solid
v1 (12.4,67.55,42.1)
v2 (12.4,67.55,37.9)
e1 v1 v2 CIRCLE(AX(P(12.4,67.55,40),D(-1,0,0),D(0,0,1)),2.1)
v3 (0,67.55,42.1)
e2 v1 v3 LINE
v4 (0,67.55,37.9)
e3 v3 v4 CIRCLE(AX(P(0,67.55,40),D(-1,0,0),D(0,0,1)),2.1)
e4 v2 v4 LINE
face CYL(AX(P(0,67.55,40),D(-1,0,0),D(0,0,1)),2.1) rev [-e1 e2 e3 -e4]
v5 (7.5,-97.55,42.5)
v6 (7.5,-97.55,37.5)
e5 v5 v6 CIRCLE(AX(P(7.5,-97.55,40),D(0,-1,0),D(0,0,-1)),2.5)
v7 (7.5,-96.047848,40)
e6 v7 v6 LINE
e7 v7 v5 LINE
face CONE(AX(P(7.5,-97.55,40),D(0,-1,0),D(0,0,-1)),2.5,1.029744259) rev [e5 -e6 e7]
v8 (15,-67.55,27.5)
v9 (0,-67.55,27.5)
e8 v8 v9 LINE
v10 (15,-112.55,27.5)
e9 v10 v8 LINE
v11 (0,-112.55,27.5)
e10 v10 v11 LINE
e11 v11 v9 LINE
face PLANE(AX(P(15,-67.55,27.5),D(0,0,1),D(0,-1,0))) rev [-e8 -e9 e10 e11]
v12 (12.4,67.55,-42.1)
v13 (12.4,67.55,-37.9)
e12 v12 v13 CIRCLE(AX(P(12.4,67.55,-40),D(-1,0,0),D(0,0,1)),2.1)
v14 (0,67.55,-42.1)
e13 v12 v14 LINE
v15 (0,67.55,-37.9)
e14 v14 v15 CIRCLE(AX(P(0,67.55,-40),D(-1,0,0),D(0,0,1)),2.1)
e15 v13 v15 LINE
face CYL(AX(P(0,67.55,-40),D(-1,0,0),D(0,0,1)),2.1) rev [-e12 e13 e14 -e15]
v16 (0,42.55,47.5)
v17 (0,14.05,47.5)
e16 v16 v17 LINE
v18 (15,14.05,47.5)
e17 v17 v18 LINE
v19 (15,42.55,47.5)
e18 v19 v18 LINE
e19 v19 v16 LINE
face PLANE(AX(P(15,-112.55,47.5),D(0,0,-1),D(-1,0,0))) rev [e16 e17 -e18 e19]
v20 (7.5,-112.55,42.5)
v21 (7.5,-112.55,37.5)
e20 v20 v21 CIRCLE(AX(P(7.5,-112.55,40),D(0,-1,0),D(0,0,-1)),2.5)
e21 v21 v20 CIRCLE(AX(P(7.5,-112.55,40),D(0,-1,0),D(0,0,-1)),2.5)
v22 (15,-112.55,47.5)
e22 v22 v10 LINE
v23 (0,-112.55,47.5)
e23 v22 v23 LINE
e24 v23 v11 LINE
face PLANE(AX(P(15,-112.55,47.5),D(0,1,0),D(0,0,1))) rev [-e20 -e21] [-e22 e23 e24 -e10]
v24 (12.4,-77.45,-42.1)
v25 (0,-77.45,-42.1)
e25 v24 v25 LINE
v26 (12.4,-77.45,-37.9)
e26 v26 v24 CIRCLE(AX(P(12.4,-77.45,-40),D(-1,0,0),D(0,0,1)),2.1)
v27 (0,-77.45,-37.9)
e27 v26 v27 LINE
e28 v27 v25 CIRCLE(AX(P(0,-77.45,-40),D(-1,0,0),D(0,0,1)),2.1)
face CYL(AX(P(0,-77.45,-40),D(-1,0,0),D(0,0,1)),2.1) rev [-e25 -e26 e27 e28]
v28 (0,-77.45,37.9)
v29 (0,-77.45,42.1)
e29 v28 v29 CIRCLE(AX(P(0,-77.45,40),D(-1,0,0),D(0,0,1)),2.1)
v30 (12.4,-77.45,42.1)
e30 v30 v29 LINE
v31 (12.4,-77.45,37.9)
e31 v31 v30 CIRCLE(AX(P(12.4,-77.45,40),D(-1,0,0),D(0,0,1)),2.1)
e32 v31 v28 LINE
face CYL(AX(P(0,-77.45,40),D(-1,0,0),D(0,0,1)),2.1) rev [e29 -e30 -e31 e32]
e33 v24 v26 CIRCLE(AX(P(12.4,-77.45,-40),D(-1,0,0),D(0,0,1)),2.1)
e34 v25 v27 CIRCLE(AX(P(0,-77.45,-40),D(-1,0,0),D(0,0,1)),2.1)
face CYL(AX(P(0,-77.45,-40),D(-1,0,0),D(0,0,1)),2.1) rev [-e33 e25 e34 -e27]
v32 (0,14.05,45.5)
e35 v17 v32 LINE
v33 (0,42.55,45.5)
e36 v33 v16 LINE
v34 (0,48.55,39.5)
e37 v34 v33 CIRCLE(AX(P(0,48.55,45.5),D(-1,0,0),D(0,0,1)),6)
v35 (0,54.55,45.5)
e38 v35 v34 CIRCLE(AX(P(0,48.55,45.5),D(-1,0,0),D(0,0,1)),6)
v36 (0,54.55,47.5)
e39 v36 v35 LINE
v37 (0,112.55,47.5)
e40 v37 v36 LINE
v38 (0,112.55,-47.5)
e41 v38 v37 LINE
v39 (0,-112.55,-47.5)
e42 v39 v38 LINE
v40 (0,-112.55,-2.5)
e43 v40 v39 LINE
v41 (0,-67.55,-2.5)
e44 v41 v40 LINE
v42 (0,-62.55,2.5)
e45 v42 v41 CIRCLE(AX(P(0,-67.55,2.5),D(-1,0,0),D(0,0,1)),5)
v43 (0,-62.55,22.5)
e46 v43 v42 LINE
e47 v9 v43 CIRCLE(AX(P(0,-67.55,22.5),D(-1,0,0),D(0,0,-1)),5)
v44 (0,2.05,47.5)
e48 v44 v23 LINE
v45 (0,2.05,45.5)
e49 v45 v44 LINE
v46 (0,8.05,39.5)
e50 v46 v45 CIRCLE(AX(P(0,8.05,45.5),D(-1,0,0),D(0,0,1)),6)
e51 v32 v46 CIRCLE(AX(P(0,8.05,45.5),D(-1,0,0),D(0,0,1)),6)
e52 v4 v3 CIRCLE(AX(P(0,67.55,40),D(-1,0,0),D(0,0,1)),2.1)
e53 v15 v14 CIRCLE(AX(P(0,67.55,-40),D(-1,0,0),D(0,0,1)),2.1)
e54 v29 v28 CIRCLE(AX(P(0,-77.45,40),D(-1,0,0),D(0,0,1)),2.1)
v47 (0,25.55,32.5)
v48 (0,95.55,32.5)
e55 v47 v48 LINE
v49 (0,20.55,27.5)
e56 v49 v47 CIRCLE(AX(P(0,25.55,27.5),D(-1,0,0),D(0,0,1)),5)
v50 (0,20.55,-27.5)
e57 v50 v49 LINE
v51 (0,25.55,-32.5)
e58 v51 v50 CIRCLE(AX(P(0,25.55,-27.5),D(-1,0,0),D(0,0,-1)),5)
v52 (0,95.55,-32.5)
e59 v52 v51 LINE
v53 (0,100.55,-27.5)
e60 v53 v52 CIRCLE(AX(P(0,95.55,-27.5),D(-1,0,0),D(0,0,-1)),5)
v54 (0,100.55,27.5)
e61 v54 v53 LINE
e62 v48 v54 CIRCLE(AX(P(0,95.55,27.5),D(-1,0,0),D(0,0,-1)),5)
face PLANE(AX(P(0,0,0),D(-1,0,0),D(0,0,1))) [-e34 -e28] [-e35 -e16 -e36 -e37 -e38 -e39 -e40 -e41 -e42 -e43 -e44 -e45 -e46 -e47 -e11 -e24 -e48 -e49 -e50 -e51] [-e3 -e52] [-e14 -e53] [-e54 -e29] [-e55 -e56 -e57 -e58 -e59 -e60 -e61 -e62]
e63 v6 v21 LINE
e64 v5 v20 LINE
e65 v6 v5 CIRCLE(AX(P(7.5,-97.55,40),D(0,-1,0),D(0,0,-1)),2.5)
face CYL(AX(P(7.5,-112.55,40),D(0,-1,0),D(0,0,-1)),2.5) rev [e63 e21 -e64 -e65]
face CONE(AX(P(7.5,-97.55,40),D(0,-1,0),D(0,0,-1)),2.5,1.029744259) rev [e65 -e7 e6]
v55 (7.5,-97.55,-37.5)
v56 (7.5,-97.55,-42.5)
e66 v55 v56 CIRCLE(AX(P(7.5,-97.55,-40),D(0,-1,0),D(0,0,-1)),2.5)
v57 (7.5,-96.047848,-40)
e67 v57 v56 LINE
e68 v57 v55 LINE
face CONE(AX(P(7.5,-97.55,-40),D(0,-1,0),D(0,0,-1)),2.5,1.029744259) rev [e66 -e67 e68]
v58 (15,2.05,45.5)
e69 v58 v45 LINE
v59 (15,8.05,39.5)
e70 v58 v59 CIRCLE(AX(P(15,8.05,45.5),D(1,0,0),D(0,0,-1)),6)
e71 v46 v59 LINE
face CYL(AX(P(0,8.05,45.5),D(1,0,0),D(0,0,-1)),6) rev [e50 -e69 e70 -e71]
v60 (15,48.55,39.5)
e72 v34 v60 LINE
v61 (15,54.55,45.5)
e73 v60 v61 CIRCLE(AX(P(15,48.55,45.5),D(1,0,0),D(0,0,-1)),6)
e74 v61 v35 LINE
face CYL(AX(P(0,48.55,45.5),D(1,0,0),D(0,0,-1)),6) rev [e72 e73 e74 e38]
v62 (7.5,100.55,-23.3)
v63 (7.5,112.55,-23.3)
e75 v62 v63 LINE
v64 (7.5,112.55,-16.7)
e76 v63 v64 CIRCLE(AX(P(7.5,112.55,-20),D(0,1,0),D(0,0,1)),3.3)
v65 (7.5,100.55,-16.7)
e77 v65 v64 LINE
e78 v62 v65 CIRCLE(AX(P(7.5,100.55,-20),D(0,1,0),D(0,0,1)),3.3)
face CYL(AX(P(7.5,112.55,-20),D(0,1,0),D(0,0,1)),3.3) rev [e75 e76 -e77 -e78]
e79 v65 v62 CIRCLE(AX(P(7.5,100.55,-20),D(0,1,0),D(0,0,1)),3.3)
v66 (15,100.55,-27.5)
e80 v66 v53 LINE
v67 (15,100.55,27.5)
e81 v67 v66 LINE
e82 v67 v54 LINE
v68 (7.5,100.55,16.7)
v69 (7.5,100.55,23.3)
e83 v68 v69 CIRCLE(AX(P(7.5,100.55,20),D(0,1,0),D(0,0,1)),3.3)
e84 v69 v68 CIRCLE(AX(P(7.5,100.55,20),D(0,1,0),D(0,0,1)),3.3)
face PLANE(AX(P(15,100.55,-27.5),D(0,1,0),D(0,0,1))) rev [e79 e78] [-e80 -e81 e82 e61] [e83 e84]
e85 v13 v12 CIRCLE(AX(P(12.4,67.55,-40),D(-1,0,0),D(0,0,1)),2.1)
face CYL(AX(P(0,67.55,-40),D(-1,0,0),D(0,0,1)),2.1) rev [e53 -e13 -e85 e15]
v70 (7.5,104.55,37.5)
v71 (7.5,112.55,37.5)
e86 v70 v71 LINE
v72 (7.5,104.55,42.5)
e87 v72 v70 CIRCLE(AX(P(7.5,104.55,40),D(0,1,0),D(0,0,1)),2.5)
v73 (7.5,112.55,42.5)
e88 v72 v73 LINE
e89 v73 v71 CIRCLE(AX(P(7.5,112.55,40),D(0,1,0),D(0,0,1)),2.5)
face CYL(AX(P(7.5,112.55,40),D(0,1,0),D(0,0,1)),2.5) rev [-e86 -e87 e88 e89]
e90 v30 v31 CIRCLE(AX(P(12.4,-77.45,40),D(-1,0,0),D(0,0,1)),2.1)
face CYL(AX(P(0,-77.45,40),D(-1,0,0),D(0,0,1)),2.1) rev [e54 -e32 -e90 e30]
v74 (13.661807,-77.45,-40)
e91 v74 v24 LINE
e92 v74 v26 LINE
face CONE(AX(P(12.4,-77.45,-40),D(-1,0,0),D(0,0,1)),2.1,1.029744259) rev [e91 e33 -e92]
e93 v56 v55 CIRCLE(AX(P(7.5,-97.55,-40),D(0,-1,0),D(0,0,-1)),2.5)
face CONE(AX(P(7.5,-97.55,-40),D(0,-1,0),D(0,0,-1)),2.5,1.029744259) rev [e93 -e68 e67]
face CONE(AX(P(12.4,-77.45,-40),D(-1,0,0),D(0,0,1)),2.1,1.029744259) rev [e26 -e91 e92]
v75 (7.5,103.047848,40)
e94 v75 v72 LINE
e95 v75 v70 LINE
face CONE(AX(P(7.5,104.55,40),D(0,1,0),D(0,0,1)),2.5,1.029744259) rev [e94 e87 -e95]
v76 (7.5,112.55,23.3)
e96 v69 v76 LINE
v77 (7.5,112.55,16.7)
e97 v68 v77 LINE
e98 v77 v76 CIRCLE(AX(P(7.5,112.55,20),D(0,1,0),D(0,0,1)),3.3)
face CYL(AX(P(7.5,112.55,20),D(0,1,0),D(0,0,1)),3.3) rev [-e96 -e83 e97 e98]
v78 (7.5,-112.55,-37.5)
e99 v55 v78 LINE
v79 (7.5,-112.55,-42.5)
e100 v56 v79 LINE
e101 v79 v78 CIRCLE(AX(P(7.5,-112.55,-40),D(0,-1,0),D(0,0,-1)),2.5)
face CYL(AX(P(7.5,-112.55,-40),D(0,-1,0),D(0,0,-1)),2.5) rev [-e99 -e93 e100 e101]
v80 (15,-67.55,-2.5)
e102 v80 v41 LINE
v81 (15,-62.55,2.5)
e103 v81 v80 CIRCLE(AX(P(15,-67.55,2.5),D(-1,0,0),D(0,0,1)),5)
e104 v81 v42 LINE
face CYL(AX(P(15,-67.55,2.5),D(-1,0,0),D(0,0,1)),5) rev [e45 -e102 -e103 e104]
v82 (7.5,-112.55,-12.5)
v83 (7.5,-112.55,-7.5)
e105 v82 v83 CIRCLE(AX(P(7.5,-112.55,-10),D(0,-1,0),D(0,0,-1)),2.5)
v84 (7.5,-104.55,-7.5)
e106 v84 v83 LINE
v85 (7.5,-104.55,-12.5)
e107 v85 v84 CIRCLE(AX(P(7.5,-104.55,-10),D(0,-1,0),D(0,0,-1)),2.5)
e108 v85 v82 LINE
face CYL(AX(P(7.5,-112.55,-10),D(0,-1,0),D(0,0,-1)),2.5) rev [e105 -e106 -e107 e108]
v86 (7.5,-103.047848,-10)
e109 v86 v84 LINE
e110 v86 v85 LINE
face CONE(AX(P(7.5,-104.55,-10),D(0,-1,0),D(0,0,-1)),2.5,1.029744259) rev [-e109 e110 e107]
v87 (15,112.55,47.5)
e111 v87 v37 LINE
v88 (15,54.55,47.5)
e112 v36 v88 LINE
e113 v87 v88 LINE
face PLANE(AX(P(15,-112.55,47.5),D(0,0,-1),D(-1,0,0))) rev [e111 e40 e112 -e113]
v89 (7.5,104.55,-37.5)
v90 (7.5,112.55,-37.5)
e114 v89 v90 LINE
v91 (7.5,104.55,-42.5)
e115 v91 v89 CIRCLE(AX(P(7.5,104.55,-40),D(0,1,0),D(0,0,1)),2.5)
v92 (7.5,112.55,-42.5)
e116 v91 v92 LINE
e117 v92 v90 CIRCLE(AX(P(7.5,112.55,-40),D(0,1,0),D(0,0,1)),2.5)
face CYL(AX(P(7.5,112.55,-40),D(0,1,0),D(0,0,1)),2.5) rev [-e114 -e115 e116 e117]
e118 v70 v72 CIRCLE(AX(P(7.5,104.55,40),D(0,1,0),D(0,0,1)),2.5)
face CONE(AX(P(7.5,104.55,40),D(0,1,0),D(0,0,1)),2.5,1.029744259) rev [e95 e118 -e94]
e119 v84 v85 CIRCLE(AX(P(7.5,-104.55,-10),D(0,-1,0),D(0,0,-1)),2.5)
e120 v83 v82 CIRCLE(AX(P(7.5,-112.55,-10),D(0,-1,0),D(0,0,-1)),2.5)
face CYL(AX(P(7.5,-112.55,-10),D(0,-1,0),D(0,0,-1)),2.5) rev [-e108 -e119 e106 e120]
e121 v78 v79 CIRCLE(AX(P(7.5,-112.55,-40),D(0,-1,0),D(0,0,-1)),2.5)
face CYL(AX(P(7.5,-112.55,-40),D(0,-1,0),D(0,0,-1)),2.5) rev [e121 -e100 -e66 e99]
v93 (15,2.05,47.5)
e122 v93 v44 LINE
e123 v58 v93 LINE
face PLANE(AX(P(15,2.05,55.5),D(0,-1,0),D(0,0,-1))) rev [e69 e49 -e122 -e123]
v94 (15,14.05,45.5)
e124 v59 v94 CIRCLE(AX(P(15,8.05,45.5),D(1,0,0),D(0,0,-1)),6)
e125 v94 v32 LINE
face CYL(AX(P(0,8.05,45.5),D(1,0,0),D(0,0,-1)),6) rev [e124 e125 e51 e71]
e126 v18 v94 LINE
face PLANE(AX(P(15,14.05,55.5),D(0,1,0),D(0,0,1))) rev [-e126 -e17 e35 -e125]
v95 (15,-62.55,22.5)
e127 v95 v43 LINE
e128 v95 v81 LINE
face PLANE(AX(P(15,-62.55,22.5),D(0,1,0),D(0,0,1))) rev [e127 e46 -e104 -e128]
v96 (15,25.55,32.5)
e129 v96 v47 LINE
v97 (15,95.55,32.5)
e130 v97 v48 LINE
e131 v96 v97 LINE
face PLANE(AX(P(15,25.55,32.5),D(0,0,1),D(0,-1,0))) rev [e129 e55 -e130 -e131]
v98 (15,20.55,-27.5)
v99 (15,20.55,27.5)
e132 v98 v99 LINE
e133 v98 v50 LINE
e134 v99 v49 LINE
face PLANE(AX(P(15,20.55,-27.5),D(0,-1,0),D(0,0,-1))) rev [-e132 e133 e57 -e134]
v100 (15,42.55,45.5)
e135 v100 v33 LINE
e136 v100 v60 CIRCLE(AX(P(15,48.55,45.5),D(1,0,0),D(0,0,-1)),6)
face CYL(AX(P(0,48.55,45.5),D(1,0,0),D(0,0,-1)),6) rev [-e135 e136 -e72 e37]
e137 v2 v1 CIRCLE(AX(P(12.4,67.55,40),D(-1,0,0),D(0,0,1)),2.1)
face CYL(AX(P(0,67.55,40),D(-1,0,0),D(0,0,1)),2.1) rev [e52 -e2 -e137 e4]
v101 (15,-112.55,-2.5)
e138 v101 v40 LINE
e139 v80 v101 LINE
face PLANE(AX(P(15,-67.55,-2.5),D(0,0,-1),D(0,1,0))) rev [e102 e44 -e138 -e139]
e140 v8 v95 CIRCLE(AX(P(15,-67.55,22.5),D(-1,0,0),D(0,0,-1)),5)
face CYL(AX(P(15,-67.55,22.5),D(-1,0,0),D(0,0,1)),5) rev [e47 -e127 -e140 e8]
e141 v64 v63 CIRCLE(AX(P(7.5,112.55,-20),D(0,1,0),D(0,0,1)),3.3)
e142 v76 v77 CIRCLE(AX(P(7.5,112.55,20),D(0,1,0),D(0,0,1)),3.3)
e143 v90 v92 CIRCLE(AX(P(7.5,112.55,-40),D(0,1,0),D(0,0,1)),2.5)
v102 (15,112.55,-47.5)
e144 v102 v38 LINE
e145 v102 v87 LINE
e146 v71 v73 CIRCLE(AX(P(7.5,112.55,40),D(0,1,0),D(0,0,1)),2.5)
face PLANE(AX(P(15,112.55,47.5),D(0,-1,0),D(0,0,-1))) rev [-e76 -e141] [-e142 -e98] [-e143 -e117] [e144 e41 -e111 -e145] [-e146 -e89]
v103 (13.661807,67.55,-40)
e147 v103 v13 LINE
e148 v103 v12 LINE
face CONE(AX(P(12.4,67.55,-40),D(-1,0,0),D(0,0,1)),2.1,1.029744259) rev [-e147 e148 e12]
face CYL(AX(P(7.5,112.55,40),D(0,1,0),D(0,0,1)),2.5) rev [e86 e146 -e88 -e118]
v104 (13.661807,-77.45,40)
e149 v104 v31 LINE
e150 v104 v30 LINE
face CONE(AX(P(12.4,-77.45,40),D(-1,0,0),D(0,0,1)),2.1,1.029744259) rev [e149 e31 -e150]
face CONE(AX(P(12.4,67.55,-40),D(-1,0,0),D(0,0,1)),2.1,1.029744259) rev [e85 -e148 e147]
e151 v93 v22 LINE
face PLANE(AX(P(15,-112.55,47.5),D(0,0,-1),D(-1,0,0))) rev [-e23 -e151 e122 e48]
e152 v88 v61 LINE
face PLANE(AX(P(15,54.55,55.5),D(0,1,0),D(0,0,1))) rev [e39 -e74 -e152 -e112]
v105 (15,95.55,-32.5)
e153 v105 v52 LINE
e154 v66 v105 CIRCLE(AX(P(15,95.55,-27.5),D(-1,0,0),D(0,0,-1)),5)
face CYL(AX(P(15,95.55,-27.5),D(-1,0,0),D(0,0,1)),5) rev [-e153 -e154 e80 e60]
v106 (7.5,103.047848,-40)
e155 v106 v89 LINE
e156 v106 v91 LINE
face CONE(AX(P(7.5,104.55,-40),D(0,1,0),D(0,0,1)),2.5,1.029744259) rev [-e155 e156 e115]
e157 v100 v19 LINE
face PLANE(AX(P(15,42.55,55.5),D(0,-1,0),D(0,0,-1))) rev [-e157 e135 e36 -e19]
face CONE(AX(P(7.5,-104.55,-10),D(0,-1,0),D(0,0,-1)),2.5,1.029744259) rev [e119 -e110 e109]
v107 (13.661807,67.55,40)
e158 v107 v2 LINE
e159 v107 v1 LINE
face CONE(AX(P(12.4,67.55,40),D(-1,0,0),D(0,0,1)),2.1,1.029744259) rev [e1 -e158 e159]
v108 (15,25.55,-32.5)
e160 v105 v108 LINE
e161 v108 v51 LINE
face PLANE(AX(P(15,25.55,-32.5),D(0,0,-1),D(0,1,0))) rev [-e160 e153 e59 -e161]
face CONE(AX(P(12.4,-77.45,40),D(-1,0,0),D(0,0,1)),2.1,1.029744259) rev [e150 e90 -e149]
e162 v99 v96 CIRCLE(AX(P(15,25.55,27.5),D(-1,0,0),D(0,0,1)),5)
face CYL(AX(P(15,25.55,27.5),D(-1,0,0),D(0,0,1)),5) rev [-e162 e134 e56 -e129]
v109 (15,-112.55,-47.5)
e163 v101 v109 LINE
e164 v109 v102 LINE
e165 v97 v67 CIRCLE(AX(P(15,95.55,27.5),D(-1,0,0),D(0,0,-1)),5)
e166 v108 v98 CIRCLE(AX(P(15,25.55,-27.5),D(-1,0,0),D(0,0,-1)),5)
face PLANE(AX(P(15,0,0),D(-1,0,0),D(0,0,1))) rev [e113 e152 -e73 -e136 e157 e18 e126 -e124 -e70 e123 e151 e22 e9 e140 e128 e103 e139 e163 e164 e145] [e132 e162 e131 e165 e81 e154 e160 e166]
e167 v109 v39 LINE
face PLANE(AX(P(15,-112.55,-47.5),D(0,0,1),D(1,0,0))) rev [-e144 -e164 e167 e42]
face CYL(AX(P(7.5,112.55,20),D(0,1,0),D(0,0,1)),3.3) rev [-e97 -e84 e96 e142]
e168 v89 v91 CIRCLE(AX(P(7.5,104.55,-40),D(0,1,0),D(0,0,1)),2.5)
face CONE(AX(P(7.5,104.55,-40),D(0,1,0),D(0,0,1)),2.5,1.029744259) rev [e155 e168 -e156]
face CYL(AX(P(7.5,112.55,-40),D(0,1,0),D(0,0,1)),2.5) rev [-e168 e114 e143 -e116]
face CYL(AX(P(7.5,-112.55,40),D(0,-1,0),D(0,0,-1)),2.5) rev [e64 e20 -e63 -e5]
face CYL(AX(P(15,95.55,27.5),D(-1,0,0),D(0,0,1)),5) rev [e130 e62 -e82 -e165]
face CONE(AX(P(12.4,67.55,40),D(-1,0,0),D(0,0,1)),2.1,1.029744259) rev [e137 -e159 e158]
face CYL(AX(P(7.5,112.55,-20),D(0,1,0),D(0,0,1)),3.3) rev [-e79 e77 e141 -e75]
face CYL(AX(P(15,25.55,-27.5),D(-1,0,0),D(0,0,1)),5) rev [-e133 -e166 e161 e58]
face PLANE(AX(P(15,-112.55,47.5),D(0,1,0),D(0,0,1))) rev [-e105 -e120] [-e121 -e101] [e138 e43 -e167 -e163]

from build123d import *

# Parameters (mm, degrees)
SKETCH1_W                  = 95
SKETCH1_H                  = 225.1
BOSS_EXTRUDE1_DEPTH        = 15
CUT_EXTRUDE1_DEPTH         = 124.080268524
M6_CLEARANCE_HOLE1_D       = 6.6
M6_CLEARANCE_HOLE1_DEPTH   = 19.75
M6_CLEARANCE_HOLE1_TIP     = 1.982840043
M6_TAPPED_HOLE1_D          = 5
M6_TAPPED_HOLE1_DEPTH      = 15
M6_TAPPED_HOLE1_TIP        = 1.502151548
F_5_0MM_BLIND_HOLE_1_D     = 5
F_5_0MM_BLIND_HOLE_1_DEPTH = 8
F_5_0MM_BLIND_HOLE_1_TIP   = 1.502151548
F_5_0MM_BLIND_HOLE_2_D     = 5
F_5_0MM_BLIND_HOLE_2_DEPTH = 8
F_5_0MM_BLIND_HOLE_2_TIP   = 1.502151548
SKETCH14_R                 = 6
CUT_EXTRUDE2_DEPTH         = 124.080268524
SKETCH15_W                 = 10
SKETCH15_H                 = 12
CUT_EXTRUDE3_DEPTH         = 124.080268524
M5_TAPPED_HOLE1_AT_2_COUNT = 2
M5_TAPPED_HOLE1_AT_2_PITCH = 145


with BuildPart() as part:
    # Sketch1 → Boss-Extrude1 (new body)
    with BuildSketch(Plane(origin=(0, 0, 0), x_dir=(0, 0, -1), z_dir=(1, 0, 0))):
        Rectangle(SKETCH1_W, SKETCH1_H)
    extrude(amount=BOSS_EXTRUDE1_DEPTH)

    # Sketch2 → Cut-Extrude1 (cut, through all)
    with BuildSketch(Plane.ZY):
        with BuildLine():
            Line((22.5, -62.55), (2.5, -62.55))
            ThreePointArc((2.5, -62.55), (-1.035533906, -64.014466094), (-2.5, -67.55))
            Line((-2.5, -67.55), (-2.5, -112.55))
            Line((-2.5, -112.55), (27.5, -112.55))
            Line((27.5, -112.55), (27.5, -67.55))
            ThreePointArc((27.5, -67.55), (26.035533906, -64.014466094), (22.5, -62.55))
        make_face()
        with BuildLine():
            Line((-27.5, 20.55), (27.5, 20.55))
            ThreePointArc((27.5, 20.55), (31.035533906, 22.014466094), (32.5, 25.55))
            Line((32.5, 25.55), (32.5, 95.55))
            ThreePointArc((32.5, 95.55), (31.035533906, 99.085533906), (27.5, 100.55))
            Line((27.5, 100.55), (-27.5, 100.55))
            ThreePointArc((-27.5, 100.55), (-31.035533906, 99.085533906), (-32.5, 95.55))
            Line((-32.5, 95.55), (-32.5, 25.55))
            ThreePointArc((-32.5, 25.55), (-31.035533906, 22.014466094), (-27.5, 20.55))
        make_face()
    extrude(amount=-CUT_EXTRUDE1_DEPTH, mode=Mode.SUBTRACT)

    # M6 Clearance Hole1
    with Locations(Plane(origin=(0, 112.55, 0), x_dir=(1, 0, 0), z_dir=(0, 1, 0))):
        with Locations((7.5, -20), (7.5, 20)):
            Hole(M6_CLEARANCE_HOLE1_D / 2, depth=M6_CLEARANCE_HOLE1_DEPTH)
            with Locations((0, 0, -(M6_CLEARANCE_HOLE1_DEPTH + M6_CLEARANCE_HOLE1_TIP / 2))):  # 118° drill point
                Cone(0, M6_CLEARANCE_HOLE1_D / 2, M6_CLEARANCE_HOLE1_TIP, mode=Mode.SUBTRACT)

    # M6 Tapped Hole1
    with Locations(Plane(origin=(0, -112.55, 0), x_dir=(-1, 0, 0), z_dir=(0, -1, 0))):
        with Locations((-7.5, -40), (-7.5, 40)):
            Hole(M6_TAPPED_HOLE1_D / 2, depth=M6_TAPPED_HOLE1_DEPTH)
            with Locations((0, 0, -(M6_TAPPED_HOLE1_DEPTH + M6_TAPPED_HOLE1_TIP / 2))):  # 118° drill point
                Cone(0, M6_TAPPED_HOLE1_D / 2, M6_TAPPED_HOLE1_TIP, mode=Mode.SUBTRACT)

    # Ø5.0mm blind hole 1
    with Locations(Plane(origin=(0, -112.55, 0), x_dir=(-1, 0, 0), z_dir=(0, -1, 0))):
        with Locations((-7.5, 10)):
            Hole(F_5_0MM_BLIND_HOLE_1_D / 2, depth=F_5_0MM_BLIND_HOLE_1_DEPTH)
            with Locations((0, 0, -(F_5_0MM_BLIND_HOLE_1_DEPTH + F_5_0MM_BLIND_HOLE_1_TIP / 2))):  # 118° drill point
                Cone(0, F_5_0MM_BLIND_HOLE_1_D / 2, F_5_0MM_BLIND_HOLE_1_TIP, mode=Mode.SUBTRACT)

    # Ø5.0mm blind hole 2
    with Locations(Plane(origin=(0, 112.55, 0), x_dir=(1, 0, 0), z_dir=(0, 1, 0))):
        with Locations((7.5, -40), (7.5, 40)):
            Hole(F_5_0MM_BLIND_HOLE_2_D / 2, depth=F_5_0MM_BLIND_HOLE_2_DEPTH)
            with Locations((0, 0, -(F_5_0MM_BLIND_HOLE_2_DEPTH + F_5_0MM_BLIND_HOLE_2_TIP / 2))):  # 118° drill point
                Cone(0, F_5_0MM_BLIND_HOLE_2_D / 2, F_5_0MM_BLIND_HOLE_2_TIP, mode=Mode.SUBTRACT)

    # Sketch14 → Cut-Extrude2 (cut, through all)
    with BuildSketch(Plane(origin=(15, 0, 0), x_dir=(0, 0, -1), z_dir=(1, 0, 0))):
        with Locations((-45.5, 48.55)):
            Circle(SKETCH14_R)
        with Locations((-45.5, 8.05)):
            Circle(SKETCH14_R)
    extrude(amount=-CUT_EXTRUDE2_DEPTH, mode=Mode.SUBTRACT)

    # Sketch15 → Cut-Extrude3 (cut, through all)
    with BuildSketch(Plane.ZY):
        with Locations((50.5, 8.05)):
            Rectangle(SKETCH15_W, SKETCH15_H)
        with Locations((50.5, 48.55)):
            Rectangle(SKETCH15_W, SKETCH15_H)
    extrude(amount=-CUT_EXTRUDE3_DEPTH, mode=Mode.SUBTRACT)

    # Sketch19 → M5 Tapped Hole1 (revolve, cut)
    with BuildSketch(Plane(origin=(0, -77.45, -40), x_dir=(0, 0, 1), z_dir=(0, 1, 0))):
        Polygon((0, 0), (0, 13.6618073), (2.1, 12.4), (2.1, 0), align=None)
    m5_tapped_hole1 = revolve(axis=Axis((-6.35, -77.45, -40), (1, 0, 0)), mode=Mode.SUBTRACT)

    # M5 Tapped Hole1 at 2: M5 Tapped Hole1 ×2
    with Locations(*[(0, i * M5_TAPPED_HOLE1_AT_2_PITCH, 0) for i in range(1, M5_TAPPED_HOLE1_AT_2_COUNT)]):
        add(m5_tapped_hole1, mode=Mode.SUBTRACT)

    # Mirror1: M5 Tapped Hole1 across plane
    add(m5_tapped_hole1.mirror(Plane.XY), mode=Mode.SUBTRACT)

    # Mirror1 copy 1 sketch → Mirror1 copy 1 (revolve, cut)
    with BuildSketch(Plane(origin=(0, 67.55, 40), x_dir=(0, 0, -1), z_dir=(0, 1, 0))):
        Polygon((0, 0), (0, -13.6618073), (2.1, -12.4), (2.1, 0), align=None)
    revolve(axis=Axis((-6.35, 67.55, 40), (-1, 0, 0)), mode=Mode.SUBTRACT)


solid = part.part
